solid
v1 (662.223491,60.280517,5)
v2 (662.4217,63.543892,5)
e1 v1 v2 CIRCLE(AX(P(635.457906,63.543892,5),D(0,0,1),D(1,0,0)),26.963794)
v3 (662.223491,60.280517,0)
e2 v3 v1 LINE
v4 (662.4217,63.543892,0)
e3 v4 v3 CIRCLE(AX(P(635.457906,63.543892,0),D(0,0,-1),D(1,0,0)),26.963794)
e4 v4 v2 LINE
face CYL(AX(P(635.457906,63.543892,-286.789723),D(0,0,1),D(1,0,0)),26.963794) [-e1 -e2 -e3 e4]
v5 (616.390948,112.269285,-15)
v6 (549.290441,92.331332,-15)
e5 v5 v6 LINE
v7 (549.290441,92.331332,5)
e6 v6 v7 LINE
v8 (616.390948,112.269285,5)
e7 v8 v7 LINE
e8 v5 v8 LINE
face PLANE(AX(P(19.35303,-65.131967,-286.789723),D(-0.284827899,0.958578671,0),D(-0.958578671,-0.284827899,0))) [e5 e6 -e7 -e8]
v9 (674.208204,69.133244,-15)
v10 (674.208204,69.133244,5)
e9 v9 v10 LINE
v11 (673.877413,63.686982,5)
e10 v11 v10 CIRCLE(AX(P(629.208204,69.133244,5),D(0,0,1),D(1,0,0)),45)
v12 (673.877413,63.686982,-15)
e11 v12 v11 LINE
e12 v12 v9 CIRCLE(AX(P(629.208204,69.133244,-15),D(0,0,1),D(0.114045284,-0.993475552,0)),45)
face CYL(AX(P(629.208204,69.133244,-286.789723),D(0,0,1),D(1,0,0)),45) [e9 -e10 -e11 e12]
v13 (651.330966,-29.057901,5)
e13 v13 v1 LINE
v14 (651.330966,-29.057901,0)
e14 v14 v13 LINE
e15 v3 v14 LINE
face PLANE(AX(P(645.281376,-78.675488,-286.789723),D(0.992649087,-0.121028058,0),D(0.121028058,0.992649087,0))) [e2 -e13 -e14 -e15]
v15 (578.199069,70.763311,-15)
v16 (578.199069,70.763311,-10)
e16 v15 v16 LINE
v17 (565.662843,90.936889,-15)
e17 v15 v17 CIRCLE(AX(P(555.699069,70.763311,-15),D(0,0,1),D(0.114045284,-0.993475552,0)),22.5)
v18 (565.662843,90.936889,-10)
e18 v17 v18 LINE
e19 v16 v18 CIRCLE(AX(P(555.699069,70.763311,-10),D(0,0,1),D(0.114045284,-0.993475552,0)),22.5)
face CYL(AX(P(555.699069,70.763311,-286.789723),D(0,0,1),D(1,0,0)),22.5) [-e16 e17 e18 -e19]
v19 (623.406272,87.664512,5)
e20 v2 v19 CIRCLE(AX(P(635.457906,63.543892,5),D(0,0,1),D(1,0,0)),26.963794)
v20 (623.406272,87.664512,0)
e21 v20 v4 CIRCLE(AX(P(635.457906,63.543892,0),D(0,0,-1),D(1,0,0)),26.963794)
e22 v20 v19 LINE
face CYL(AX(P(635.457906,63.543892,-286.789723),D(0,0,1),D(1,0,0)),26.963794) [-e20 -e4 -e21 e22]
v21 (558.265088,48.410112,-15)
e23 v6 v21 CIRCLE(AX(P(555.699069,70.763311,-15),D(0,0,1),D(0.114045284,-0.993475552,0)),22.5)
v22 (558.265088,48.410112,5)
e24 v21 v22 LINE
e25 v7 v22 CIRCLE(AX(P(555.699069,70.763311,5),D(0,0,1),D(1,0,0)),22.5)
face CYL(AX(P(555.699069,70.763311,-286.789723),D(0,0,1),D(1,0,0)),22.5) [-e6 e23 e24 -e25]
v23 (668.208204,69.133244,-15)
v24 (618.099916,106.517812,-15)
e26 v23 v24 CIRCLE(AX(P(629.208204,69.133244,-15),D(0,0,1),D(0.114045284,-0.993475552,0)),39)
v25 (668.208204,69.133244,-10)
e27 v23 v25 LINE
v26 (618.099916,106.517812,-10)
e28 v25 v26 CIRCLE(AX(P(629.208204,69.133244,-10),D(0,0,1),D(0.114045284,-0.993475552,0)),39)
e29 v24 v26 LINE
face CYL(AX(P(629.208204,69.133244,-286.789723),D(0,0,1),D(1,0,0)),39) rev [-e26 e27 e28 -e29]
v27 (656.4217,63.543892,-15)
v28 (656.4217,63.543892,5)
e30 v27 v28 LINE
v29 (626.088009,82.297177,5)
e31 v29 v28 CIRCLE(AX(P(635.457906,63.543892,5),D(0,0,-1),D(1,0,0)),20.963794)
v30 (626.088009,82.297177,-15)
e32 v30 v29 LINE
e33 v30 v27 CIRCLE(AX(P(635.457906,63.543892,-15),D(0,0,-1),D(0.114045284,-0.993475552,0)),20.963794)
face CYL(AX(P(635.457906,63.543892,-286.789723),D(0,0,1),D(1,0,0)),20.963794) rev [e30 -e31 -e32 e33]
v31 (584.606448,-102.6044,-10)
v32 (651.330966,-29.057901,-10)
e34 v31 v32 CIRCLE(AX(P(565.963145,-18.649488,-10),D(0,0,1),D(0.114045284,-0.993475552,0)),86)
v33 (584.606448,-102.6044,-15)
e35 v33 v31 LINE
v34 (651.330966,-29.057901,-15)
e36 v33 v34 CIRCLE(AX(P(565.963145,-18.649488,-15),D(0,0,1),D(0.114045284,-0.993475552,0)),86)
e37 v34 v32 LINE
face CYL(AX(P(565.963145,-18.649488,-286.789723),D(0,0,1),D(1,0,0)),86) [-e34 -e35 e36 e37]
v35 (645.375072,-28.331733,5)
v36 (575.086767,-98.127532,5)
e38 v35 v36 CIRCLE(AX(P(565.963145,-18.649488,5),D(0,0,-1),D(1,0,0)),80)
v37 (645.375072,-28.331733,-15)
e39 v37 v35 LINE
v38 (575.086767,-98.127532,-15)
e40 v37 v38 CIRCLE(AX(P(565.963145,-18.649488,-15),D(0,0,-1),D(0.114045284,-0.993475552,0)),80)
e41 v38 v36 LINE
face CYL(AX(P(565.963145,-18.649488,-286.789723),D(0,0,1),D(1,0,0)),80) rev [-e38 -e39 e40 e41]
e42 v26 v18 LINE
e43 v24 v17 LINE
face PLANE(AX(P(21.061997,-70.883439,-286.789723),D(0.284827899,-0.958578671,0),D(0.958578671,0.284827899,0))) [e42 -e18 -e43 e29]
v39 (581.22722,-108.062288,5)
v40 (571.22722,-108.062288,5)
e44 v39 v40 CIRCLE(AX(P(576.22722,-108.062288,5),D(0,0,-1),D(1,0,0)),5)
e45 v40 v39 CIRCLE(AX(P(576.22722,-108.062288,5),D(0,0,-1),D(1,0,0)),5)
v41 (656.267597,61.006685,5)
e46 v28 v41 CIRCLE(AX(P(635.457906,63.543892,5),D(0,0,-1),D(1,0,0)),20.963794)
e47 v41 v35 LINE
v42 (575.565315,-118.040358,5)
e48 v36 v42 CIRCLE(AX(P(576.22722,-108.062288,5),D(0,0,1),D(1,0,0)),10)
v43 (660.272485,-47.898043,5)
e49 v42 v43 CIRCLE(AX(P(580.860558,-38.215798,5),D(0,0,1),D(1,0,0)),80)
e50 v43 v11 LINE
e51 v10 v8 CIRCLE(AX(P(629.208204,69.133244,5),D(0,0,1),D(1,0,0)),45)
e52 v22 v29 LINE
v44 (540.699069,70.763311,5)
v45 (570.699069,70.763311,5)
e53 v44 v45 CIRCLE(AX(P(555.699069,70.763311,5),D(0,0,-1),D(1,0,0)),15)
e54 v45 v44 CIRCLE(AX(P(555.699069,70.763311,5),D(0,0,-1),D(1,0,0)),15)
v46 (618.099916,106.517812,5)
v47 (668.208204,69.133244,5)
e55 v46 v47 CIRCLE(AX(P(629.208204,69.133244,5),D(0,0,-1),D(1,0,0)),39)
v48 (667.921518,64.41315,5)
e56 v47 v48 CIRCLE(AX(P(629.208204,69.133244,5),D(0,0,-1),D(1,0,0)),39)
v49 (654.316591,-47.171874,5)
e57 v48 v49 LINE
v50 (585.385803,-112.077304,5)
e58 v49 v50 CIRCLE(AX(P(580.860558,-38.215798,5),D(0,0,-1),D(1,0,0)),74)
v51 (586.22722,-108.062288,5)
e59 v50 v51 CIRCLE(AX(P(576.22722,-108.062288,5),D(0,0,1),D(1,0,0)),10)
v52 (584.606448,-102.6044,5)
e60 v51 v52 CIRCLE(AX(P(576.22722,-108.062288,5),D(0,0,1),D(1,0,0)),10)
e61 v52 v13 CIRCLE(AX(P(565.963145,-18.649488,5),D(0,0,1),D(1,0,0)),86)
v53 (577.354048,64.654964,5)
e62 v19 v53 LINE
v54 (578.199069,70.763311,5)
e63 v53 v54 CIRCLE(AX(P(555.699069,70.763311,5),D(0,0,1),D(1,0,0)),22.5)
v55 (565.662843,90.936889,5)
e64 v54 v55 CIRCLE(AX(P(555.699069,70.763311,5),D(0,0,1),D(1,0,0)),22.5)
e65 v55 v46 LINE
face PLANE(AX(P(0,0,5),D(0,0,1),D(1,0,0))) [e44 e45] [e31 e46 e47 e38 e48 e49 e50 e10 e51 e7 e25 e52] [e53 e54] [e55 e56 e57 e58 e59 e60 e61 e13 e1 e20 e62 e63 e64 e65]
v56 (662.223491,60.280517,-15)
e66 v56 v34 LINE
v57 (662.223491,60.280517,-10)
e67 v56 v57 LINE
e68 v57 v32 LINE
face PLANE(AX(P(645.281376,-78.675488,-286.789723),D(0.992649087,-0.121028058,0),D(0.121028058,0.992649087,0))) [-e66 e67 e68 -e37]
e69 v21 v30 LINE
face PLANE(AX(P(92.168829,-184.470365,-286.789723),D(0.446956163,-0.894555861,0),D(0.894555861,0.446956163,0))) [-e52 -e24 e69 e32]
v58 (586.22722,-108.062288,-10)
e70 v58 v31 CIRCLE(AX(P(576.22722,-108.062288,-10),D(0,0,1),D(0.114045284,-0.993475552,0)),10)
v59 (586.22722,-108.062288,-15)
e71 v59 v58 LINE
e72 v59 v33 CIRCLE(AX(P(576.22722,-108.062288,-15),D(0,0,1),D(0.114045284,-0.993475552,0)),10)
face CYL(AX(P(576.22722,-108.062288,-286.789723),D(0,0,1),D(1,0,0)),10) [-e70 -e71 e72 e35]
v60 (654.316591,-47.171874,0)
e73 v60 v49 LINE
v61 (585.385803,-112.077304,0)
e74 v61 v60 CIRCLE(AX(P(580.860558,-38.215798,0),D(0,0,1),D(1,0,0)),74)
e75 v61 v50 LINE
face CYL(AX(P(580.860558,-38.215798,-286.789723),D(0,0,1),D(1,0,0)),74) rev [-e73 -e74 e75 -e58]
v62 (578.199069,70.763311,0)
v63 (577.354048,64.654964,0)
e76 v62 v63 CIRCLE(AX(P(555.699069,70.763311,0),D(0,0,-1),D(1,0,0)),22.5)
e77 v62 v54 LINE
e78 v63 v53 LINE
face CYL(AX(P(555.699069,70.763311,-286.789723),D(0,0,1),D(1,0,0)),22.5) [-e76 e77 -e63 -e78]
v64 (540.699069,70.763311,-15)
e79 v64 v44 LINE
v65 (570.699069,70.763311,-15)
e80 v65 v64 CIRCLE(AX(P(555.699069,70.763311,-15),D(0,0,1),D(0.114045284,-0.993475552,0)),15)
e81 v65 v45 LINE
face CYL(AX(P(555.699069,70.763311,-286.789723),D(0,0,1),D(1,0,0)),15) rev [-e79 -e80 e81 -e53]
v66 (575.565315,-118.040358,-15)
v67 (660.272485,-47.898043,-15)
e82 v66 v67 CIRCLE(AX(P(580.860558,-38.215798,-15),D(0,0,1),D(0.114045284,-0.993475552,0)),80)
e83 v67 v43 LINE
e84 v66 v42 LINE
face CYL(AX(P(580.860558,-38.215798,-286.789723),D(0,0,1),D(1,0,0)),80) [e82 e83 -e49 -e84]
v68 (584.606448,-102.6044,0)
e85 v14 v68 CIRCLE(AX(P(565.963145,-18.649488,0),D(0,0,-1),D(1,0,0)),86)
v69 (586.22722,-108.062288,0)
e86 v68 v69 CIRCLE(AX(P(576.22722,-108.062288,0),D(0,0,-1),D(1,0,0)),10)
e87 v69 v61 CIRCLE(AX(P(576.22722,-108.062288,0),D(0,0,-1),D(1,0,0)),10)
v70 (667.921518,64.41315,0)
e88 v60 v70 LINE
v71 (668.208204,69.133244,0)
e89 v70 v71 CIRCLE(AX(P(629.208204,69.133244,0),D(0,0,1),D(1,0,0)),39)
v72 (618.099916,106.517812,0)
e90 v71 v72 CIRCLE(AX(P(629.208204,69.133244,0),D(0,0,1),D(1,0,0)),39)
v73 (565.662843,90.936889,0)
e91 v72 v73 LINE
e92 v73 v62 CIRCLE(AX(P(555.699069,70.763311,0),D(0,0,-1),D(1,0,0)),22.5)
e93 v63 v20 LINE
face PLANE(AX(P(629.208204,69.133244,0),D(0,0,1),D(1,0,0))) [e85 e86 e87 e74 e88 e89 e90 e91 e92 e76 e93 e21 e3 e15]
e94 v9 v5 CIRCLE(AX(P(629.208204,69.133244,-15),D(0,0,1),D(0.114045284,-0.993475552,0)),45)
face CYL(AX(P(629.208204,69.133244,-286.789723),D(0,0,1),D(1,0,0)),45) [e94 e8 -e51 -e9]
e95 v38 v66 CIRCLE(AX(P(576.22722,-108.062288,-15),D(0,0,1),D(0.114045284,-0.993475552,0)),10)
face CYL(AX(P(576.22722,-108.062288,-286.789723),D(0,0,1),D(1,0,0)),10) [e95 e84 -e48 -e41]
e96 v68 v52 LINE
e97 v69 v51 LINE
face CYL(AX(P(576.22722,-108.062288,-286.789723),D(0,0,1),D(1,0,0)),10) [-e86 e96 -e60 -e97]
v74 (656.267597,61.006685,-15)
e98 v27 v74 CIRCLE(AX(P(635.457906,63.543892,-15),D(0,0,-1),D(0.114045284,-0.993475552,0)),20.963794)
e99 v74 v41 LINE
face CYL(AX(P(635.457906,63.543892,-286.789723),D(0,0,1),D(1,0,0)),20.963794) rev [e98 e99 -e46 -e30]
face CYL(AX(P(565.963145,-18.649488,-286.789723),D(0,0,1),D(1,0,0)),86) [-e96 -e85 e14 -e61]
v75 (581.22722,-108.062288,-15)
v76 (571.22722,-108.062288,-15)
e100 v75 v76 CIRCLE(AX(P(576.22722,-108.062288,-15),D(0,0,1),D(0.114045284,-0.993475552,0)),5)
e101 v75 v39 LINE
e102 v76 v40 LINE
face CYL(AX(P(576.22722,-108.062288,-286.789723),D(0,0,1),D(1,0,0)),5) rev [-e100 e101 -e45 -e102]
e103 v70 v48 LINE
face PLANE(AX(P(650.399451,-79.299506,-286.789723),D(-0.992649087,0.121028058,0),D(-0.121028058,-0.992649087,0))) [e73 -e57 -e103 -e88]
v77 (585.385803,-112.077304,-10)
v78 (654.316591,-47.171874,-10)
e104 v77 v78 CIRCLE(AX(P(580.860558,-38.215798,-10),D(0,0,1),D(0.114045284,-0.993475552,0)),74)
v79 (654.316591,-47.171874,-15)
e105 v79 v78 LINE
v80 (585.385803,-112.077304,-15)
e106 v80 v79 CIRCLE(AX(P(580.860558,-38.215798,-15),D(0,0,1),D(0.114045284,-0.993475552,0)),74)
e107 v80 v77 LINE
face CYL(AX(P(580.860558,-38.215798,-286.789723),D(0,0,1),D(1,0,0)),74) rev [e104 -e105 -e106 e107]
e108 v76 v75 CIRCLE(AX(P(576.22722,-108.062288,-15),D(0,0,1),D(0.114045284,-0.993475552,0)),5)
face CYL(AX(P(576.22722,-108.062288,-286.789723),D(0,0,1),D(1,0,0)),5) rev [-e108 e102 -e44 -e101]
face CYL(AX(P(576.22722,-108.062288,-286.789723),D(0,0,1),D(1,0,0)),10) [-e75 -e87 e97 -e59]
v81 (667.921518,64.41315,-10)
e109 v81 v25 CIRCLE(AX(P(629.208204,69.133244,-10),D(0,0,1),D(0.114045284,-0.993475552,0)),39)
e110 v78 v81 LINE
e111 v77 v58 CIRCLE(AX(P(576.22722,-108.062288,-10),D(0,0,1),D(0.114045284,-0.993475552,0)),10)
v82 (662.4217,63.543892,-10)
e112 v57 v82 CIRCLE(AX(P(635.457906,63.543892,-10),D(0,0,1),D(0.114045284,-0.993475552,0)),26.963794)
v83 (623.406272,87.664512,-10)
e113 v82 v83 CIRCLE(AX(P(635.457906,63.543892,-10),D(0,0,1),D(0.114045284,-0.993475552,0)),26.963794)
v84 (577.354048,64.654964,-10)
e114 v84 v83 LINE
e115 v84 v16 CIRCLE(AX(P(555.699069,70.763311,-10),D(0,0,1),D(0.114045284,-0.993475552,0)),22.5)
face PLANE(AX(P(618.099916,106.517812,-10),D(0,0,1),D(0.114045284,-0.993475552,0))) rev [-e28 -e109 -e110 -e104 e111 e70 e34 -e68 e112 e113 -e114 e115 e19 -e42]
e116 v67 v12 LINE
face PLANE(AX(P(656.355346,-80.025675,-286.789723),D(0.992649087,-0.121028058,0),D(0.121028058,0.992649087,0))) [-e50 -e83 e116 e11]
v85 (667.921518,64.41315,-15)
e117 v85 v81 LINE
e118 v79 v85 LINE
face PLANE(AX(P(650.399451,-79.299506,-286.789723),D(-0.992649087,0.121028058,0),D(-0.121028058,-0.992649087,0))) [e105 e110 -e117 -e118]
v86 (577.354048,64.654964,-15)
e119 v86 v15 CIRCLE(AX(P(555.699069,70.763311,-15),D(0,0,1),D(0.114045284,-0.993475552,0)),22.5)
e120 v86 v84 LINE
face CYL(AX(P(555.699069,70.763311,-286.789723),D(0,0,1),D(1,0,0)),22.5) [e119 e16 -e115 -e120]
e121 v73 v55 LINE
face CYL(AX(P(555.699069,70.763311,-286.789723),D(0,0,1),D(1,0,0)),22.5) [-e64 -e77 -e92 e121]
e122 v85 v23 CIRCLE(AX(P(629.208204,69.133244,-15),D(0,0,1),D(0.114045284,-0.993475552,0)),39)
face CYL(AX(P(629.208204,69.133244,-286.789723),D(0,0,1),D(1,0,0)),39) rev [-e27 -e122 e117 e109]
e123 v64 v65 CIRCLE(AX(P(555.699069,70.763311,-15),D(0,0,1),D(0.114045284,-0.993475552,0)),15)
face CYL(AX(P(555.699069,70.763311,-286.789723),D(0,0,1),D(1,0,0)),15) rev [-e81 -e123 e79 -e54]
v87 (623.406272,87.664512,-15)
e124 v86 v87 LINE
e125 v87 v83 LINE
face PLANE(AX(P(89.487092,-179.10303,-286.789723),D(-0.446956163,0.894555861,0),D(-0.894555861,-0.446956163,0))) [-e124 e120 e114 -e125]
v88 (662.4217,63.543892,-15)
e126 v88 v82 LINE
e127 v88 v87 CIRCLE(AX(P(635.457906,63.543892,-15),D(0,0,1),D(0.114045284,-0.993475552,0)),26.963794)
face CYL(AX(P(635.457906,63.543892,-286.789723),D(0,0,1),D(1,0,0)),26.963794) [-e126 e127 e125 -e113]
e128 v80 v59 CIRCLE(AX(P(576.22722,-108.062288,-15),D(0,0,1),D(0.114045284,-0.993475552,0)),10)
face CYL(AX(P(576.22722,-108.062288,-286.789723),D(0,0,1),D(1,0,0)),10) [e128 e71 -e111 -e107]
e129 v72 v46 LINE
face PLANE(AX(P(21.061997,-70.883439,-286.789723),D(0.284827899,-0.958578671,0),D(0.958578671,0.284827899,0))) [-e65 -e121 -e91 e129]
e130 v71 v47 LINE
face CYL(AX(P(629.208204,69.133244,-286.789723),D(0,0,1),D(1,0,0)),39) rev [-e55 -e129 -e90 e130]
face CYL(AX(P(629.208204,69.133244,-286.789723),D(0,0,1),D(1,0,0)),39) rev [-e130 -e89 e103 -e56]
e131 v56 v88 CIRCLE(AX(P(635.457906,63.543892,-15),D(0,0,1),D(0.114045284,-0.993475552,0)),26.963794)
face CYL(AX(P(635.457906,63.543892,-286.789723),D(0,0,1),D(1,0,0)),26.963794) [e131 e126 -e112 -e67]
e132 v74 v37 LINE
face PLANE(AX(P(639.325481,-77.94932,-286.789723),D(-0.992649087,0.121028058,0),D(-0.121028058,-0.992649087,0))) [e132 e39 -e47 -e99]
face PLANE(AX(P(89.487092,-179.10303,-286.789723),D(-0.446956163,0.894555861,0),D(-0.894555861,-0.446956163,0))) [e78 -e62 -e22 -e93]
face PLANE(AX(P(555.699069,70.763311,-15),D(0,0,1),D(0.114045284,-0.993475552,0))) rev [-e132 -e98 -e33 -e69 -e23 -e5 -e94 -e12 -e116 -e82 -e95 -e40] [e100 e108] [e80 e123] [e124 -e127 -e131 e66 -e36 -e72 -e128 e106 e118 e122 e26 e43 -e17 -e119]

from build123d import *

# Parameters (mm, degrees)
BOSS_EXTRUDE1_DEPTH = 10
BOSS_EXTRUDE2_DEPTH = 20


with BuildPart() as part:
    # Sketch2 → Boss-Extrude1 (new body)
    with BuildSketch(Plane.XY):
        with BuildLine():
            Line((618.099915724, 106.517812479), (565.662842819, 90.936888582))
            ThreePointArc((565.662842819, 90.936888582), (576.256823377, 79.908186522), (577.354047602, 64.654964167))
            Line((577.354047602, 64.654964167), (623.40627245, 87.664511809))
            ThreePointArc((623.40627245, 87.664511809), (651.001261382, 85.576828369), (662.223491353, 60.280516566))
            Line((662.223491353, 60.280516566), (651.330966137, -29.057901231))
            ThreePointArc((651.330966137, -29.057901231), (629.656554116, -76.434863517), (584.606448191, -102.60440016))
            ThreePointArc((584.606448191, -102.60440016), (586.193547668, -107.242337985), (585.385803247, -112.077304476))
            ThreePointArc((585.385803247, -112.077304476), (631.589727703, -92.09112966), (654.31659075, -47.171874157))
            Line((654.31659075, -47.171874157), (667.921518172, 64.413150063))
            ThreePointArc((667.921518172, 64.413150063), (654.381801444, 98.92065746), (618.099915724, 106.517812479))
        make_face()
    extrude(amount=-BOSS_EXTRUDE1_DEPTH)

    # Sketch3 → Boss-Extrude2 (add)
    with BuildSketch(Plane.XY.offset(5)):
        with BuildLine():
            Line((616.390948328, 112.269284503), (549.290441383, 92.331331557))
            ThreePointArc((549.290441383, 92.331331557), (533.654573144, 66.258847309), (558.265088008, 48.410111539))
            Line((558.265088008, 48.410111539), (626.088009426, 82.297176642))
            ThreePointArc((626.088009426, 82.297176642), (647.542544399, 80.674045809), (656.267596834, 61.006684914))
            Line((656.267596834, 61.006684914), (645.375071617, -28.331732883))
            ThreePointArc((645.375071617, -28.331732883), (622.332456349, -75.416562354), (575.086767417, -98.127532436))
            ThreePointArc((575.086767417, -98.127532436), (566.230106721, -108.302539786), (575.565314818, -118.040357973))
            ThreePointArc((575.565314818, -118.040357973), (631.883168962, -99.833110413), (660.27248527, -47.898042505))
            Line((660.27248527, -47.898042505), (673.877412692, 63.686981716))
            ThreePointArc((673.877412692, 63.686981716), (658.254662621, 103.503336404), (616.390948328, 112.269284503))
        make_face()
        with BuildLine():
            ThreePointArc((618.099915724, 106.517812479), (654.381801444, 98.92065746), (667.921518172, 64.413150063))
            Line((667.921518172, 64.413150063), (654.31659075, -47.171874157))
            ThreePointArc((654.31659075, -47.171874157), (631.589727703, -92.09112966), (585.385803247, -112.077304476))
            ThreePointArc((585.385803247, -112.077304476), (586.193547668, -107.242337985), (584.606448191, -102.60440016))
            ThreePointArc((584.606448191, -102.60440016), (629.656554116, -76.434863517), (651.330966137, -29.057901231))
            Line((651.330966137, -29.057901231), (662.223491353, 60.280516566))
            ThreePointArc((662.223491353, 60.280516566), (651.001261382, 85.576828369), (623.40627245, 87.664511809))
            Line((623.40627245, 87.664511809), (577.354047602, 64.654964167))
            ThreePointArc((577.354047602, 64.654964167), (576.256823377, 79.908186522), (565.662842819, 90.936888582))
            Line((565.662842819, 90.936888582), (618.099915724, 106.517812479))
        make_face(mode=Mode.SUBTRACT)
        with BuildLine():
            ThreePointArc((557.409748377, 55.861178182), (540.79693583, 69.052632206), (553.988389854, 85.665444753))
            ThreePointArc((553.988389854, 85.665444753), (570.601202401, 72.47399073), (557.409748377, 55.861178182))
        make_face(mode=Mode.SUBTRACT)
        with BuildLine():
            ThreePointArc((576.797446678, -113.029665722), (571.259842496, -108.632514381), (575.656993837, -103.094910198))
            ThreePointArc((575.656993837, -103.094910198), (581.19459802, -107.492061539), (576.797446678, -113.029665722))
        make_face(mode=Mode.SUBTRACT)
    extrude(amount=-BOSS_EXTRUDE2_DEPTH)


solid = part.part
